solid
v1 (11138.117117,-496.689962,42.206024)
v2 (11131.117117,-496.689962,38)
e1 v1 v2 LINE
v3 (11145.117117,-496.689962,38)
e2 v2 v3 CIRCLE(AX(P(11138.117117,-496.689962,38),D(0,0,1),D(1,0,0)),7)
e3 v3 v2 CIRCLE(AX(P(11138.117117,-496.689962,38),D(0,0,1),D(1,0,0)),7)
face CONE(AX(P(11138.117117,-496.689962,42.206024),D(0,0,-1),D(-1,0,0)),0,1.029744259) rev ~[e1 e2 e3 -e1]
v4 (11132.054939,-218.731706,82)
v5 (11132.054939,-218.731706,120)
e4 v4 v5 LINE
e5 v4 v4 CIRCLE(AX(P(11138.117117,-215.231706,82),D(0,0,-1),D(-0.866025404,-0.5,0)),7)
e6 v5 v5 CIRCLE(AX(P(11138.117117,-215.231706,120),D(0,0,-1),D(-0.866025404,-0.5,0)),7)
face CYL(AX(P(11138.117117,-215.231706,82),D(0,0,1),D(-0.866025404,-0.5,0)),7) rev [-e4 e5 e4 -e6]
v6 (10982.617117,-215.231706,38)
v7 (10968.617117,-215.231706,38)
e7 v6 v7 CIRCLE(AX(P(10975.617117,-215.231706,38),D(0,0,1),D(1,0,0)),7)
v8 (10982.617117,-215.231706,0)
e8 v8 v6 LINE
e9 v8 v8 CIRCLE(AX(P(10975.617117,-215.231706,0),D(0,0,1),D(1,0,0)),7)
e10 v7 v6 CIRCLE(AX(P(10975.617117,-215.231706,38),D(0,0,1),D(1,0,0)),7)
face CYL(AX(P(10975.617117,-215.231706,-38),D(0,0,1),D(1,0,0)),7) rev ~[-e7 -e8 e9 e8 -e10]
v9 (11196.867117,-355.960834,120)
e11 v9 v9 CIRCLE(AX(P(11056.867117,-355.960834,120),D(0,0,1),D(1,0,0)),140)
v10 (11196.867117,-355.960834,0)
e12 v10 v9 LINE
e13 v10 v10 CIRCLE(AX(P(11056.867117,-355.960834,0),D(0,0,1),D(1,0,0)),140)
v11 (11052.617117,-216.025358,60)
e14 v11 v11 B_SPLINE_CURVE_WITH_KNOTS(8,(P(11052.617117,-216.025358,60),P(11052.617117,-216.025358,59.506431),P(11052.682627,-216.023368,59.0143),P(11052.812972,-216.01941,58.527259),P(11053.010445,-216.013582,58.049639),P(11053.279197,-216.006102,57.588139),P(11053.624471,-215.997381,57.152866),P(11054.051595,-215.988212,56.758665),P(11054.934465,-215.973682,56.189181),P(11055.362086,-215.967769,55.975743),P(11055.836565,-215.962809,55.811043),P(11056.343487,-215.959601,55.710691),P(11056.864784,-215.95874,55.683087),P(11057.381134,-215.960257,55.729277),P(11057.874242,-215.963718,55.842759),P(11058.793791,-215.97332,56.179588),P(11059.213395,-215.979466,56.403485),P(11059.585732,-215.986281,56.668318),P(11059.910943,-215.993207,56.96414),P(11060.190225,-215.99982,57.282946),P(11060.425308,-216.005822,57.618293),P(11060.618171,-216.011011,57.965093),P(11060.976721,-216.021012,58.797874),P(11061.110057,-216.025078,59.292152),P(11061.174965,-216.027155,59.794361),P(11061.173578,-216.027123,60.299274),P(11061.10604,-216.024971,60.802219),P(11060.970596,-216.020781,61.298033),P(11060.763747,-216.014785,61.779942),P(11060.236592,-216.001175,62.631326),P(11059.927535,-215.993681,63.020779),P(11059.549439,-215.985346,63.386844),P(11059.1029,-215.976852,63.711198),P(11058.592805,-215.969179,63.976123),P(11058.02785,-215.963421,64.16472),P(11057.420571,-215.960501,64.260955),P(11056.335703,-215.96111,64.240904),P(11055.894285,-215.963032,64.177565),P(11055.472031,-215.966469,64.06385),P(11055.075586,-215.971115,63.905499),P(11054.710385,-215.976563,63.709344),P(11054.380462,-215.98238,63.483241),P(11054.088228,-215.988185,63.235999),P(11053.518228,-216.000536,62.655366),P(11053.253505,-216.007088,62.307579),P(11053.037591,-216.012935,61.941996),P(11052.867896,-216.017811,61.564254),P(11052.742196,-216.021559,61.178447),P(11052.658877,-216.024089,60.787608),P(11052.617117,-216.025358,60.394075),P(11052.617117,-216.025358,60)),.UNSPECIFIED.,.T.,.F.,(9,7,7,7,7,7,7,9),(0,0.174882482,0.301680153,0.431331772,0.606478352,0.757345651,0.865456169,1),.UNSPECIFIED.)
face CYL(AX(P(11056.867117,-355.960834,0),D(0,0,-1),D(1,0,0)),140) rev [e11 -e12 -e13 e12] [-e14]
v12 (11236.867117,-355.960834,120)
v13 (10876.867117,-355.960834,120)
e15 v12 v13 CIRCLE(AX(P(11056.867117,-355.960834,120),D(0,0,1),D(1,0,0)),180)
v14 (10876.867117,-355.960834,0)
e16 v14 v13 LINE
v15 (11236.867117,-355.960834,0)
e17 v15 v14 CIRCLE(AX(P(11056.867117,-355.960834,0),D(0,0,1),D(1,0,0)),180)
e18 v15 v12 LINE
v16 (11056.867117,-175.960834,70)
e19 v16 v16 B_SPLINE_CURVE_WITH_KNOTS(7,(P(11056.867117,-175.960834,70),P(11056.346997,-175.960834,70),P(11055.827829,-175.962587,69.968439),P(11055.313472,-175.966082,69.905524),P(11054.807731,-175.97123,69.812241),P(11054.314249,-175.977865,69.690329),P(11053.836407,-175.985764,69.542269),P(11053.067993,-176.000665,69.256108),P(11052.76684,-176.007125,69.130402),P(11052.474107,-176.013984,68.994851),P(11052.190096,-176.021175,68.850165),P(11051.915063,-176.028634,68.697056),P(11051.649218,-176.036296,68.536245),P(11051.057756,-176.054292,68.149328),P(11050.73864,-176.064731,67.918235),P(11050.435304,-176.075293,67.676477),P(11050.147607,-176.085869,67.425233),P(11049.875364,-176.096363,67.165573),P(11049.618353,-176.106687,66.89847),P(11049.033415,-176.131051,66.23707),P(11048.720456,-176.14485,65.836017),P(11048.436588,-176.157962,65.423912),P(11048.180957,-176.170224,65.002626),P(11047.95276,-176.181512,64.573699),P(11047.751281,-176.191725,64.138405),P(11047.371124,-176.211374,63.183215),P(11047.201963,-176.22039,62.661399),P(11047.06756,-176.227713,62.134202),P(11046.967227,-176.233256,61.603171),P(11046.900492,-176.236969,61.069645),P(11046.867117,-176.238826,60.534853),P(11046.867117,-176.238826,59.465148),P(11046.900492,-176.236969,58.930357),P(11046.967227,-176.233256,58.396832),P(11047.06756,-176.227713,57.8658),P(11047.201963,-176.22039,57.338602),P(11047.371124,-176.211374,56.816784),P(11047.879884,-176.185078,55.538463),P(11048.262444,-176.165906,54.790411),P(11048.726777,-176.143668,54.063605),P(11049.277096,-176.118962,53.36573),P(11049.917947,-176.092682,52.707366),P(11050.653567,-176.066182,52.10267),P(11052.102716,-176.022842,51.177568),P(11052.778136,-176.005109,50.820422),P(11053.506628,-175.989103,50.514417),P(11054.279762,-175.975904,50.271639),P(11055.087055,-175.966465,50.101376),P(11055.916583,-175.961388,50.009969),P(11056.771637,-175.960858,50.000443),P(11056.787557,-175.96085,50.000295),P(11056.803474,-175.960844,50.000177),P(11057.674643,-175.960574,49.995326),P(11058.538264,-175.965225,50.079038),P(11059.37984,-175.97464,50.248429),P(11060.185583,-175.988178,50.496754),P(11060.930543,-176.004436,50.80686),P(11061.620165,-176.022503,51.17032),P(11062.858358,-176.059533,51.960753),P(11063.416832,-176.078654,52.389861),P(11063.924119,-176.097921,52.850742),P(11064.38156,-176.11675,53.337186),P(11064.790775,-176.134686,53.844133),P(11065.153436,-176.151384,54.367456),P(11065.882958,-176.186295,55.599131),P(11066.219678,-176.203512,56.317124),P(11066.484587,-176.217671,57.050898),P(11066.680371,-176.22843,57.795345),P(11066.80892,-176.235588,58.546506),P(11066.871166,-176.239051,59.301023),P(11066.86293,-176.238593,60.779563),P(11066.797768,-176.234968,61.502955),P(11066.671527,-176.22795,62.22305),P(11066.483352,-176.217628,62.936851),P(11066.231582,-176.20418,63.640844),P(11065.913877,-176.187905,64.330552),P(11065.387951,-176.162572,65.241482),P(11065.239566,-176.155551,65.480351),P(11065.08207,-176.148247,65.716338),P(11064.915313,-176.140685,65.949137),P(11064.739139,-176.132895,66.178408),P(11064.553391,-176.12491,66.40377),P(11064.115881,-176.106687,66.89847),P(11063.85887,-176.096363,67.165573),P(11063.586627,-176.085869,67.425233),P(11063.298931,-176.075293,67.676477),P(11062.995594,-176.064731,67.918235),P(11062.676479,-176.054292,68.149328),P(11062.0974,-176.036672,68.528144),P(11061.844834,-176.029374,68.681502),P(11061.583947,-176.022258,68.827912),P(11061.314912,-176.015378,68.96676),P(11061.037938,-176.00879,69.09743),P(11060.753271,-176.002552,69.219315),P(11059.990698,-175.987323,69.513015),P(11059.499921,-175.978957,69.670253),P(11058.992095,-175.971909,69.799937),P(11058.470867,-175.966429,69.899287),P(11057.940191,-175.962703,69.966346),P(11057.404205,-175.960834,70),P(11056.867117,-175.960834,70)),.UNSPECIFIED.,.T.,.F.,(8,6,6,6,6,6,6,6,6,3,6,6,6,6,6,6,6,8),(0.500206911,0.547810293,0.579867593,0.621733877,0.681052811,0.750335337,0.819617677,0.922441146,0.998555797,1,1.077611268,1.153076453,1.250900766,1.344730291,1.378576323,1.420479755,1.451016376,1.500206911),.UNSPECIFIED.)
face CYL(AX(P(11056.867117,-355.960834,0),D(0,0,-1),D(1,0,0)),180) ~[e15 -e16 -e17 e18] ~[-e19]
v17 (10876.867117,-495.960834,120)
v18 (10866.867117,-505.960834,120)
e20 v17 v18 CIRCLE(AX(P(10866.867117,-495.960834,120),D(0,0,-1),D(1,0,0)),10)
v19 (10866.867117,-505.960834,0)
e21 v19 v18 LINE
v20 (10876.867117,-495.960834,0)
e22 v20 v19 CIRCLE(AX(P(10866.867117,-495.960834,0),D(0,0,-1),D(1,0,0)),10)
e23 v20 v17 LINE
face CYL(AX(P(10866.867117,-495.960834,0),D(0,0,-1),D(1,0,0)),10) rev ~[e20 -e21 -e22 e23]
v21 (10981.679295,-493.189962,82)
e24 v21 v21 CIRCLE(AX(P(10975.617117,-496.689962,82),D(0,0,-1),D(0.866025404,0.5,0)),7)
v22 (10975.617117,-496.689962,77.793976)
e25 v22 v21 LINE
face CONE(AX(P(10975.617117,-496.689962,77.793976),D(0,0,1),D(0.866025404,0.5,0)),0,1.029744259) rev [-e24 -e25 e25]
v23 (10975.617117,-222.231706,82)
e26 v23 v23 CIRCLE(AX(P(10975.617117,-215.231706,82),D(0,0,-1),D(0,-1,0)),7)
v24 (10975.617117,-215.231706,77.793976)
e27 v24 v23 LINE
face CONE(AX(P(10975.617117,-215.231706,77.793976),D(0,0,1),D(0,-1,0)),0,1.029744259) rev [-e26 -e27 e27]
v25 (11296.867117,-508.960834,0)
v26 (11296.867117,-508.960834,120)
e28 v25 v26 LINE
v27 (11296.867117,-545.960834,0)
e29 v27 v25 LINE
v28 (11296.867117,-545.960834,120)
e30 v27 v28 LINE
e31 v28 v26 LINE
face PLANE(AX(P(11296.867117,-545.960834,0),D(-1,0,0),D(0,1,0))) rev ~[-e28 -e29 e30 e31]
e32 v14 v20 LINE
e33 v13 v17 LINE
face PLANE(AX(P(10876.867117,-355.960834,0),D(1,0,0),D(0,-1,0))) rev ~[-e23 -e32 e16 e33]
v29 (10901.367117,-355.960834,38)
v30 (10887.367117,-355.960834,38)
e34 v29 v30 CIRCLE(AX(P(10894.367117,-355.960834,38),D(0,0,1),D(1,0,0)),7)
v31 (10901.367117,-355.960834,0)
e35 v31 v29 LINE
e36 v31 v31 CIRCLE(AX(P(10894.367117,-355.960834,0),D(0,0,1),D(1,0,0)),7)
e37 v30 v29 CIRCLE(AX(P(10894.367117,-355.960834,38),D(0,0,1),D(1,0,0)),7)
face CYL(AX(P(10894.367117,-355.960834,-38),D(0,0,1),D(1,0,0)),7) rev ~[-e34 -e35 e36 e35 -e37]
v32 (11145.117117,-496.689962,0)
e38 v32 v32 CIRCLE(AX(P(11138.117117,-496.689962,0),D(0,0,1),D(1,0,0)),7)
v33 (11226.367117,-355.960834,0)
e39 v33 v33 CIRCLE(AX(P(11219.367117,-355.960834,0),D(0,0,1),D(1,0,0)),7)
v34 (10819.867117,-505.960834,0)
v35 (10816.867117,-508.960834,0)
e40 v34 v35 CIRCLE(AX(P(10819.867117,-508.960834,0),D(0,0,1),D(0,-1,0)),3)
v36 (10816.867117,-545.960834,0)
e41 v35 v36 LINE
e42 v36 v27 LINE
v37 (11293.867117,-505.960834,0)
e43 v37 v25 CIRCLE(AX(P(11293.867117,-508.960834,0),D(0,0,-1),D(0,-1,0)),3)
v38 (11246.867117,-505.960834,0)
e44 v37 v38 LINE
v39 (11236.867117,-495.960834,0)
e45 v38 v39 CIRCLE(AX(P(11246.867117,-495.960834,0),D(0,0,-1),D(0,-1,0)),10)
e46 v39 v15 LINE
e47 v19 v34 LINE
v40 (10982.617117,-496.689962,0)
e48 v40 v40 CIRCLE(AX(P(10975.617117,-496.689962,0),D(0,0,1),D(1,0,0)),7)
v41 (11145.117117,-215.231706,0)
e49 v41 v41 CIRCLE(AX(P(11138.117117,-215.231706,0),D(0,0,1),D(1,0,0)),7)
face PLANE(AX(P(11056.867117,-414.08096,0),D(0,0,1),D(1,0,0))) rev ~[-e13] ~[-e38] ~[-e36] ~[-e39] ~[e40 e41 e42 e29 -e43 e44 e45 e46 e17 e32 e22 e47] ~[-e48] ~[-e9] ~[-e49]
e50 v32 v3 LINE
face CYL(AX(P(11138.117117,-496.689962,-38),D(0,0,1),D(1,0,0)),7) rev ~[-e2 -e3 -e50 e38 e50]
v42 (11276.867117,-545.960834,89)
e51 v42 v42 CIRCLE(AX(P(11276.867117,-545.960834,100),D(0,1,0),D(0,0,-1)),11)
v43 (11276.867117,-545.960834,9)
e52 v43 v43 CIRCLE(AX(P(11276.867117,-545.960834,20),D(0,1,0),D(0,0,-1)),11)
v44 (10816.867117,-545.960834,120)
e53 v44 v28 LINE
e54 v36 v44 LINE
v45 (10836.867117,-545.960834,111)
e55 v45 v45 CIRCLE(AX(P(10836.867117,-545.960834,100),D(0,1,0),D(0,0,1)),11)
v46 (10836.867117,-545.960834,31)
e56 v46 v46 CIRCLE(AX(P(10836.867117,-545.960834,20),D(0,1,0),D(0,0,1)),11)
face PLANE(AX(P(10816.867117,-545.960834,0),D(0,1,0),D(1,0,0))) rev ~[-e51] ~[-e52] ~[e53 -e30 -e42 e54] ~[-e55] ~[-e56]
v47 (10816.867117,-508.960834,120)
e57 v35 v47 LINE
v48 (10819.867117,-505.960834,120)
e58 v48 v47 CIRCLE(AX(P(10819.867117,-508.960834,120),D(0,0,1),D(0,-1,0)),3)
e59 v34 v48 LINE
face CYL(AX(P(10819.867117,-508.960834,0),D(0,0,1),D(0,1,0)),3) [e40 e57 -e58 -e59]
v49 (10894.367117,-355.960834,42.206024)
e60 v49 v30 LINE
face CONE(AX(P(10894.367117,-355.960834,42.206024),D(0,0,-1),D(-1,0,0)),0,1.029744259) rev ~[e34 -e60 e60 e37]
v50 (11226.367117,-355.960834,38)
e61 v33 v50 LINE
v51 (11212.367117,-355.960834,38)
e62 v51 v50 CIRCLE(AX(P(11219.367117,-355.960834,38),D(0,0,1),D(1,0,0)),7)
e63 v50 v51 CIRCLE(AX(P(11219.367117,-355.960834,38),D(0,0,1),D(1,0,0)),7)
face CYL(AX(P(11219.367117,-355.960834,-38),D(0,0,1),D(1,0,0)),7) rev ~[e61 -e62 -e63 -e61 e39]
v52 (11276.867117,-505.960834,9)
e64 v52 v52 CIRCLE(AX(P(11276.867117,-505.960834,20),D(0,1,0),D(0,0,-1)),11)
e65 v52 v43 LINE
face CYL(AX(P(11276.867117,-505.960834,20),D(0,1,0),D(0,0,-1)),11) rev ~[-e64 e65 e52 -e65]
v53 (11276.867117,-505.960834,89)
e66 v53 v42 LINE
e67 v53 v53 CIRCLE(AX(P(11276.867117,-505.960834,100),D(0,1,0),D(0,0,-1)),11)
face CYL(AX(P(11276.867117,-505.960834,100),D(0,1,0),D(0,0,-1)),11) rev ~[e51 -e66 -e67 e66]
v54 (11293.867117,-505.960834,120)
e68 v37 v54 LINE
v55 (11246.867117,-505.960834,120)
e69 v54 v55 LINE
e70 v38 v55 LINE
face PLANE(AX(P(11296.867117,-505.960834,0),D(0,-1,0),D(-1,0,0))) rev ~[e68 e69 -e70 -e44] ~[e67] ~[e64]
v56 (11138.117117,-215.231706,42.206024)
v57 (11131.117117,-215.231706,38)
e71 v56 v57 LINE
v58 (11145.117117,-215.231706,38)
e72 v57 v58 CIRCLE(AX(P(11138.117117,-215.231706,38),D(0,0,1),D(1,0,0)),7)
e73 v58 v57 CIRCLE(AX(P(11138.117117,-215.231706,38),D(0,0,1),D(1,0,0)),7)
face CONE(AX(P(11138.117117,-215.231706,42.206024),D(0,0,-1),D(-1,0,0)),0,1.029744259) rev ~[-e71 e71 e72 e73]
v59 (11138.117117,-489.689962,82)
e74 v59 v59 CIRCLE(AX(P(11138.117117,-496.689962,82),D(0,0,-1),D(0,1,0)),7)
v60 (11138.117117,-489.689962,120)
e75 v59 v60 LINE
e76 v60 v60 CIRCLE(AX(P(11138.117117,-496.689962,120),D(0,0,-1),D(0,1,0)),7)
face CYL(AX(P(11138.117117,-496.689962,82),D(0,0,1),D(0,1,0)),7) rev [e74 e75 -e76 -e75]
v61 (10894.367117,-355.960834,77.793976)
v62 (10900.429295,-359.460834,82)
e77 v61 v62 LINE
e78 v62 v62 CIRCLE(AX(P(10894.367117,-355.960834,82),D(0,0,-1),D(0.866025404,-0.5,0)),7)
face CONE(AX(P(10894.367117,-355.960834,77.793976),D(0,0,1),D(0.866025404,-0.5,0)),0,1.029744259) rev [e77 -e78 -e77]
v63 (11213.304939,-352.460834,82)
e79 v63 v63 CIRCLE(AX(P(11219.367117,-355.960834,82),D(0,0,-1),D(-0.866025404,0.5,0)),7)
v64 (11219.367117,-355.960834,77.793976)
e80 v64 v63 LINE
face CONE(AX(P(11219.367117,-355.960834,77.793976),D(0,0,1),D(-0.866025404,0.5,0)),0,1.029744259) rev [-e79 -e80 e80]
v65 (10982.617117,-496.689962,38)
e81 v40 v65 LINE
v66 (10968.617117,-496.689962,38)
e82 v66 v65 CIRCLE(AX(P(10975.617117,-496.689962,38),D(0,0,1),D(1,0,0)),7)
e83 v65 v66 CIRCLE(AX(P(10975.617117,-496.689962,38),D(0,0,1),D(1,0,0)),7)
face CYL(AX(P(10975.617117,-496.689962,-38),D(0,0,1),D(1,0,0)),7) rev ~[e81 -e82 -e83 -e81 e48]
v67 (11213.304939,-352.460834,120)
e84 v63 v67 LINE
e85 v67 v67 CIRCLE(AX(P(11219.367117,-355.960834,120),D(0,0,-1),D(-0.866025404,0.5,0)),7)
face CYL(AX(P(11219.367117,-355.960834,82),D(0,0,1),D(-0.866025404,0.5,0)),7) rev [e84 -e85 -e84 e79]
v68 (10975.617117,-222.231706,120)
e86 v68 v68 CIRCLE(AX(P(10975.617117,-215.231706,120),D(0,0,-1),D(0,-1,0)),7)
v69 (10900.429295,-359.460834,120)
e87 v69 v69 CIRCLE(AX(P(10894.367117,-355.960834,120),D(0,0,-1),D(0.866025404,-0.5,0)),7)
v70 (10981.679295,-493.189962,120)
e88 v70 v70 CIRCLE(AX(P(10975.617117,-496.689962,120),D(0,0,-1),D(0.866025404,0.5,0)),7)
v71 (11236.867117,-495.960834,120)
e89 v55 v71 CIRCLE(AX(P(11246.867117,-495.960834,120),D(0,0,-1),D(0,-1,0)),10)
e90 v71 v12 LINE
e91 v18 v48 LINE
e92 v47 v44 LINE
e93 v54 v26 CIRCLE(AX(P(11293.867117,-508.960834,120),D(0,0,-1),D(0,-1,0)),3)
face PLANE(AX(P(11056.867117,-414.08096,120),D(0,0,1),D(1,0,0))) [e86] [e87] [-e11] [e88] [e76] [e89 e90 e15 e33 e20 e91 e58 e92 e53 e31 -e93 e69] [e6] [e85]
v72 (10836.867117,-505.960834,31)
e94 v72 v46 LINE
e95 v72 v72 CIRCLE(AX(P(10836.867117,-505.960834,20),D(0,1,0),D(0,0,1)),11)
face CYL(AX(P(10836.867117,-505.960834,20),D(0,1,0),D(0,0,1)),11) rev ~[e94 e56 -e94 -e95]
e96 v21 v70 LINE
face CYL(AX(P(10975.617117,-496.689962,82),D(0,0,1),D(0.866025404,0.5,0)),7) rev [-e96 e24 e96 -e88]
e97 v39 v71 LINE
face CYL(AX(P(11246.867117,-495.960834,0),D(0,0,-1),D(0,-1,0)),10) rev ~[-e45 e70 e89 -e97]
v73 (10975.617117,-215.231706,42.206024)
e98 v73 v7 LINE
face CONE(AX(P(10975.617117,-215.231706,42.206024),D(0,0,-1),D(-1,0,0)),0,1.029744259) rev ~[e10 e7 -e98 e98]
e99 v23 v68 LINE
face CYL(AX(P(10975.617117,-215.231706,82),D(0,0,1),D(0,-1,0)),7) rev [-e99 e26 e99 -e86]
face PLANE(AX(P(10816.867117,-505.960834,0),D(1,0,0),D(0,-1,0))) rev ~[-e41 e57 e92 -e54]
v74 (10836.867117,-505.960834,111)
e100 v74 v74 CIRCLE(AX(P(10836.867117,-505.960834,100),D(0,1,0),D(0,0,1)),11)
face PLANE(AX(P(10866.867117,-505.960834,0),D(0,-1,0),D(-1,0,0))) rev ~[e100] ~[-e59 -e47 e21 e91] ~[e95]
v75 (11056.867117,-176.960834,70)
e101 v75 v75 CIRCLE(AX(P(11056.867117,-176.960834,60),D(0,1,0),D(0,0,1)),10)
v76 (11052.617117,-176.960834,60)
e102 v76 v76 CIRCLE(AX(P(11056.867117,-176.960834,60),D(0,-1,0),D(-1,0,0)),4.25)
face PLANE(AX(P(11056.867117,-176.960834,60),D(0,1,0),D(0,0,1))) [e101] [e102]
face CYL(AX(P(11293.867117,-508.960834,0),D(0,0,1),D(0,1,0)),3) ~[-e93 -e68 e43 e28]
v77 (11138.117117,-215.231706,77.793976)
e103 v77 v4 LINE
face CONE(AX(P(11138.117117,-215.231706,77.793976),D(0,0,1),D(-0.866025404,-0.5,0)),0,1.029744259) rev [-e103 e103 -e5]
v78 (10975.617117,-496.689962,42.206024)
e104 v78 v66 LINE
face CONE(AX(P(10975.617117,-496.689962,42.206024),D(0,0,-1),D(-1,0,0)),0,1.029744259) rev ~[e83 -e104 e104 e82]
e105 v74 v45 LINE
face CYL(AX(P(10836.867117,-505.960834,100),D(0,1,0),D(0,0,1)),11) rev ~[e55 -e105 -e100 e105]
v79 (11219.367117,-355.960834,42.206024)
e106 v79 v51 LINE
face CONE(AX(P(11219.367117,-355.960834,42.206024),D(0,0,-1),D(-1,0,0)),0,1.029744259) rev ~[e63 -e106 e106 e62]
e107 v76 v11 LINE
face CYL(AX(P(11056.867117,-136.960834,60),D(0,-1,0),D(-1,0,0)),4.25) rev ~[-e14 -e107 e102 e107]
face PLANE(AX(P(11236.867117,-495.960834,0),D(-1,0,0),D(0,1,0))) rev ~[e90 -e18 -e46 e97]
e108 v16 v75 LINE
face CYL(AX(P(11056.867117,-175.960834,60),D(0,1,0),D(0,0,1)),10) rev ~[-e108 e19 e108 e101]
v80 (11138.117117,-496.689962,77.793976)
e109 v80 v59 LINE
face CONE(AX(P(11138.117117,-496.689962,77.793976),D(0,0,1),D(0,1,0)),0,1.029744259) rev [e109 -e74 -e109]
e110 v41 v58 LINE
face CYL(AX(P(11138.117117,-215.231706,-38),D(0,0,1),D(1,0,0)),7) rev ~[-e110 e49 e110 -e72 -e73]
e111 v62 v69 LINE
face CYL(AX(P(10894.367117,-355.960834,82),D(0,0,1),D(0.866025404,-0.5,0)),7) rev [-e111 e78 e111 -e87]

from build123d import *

# Parameters (mm, degrees)
SKETCH1_R              = 140
BOSS_EXTRUDE1_DEPTH    = 120
SKETCH3_R              = 10
CUT_EXTRUDE1_DEPTH     = 1
M10_TAPPED_HOLE1_D     = 8.5
M10_TAPPED_HOLE1_DEPTH = 40
M10_TAPPED_HOLE1_TIP   = 2.553657631
SKETCH7_R              = 11
CUT_EXTRUDE2_DEPTH     = 11303.32306496
FILLET1_R              = 3
CIRPATTERN1_COUNT      = 6
M16_TAPPED_HOLE2_D     = 14
M16_TAPPED_HOLE2_DEPTH = 38
M16_TAPPED_HOLE2_TIP   = 4.206024333


with BuildPart() as part:
    # Sketch1 → Boss-Extrude1 (new body)
    with BuildSketch(Plane.XY):
        with BuildLine():
            Line((10876.867117242, -355.960833708), (10876.867117242, -495.960833708))
            ThreePointArc((10876.867117242, -495.960833708), (10873.938185054, -503.03190152), (10866.867117242, -505.960833708))
            Line((10866.867117242, -505.960833708), (10816.867117242, -505.960833708))
            Line((10816.867117242, -505.960833708), (10816.867117242, -545.960833708))
            Line((10816.867117242, -545.960833708), (11296.867117242, -545.960833708))
            Line((11296.867117242, -545.960833708), (11296.867117242, -505.960833708))
            Line((11296.867117242, -505.960833708), (11246.867117242, -505.960833708))
            ThreePointArc((11246.867117242, -505.960833708), (11239.796049431, -503.03190152), (11236.867117242, -495.960833708))
            Line((11236.867117242, -495.960833708), (11236.867117242, -355.960833708))
            ThreePointArc((11236.867117242, -355.960833708), (11056.867117242, -175.960833708), (10876.867117242, -355.960833708))
        make_face()
        with Locations((11056.867117242, -355.960833708)):
            Circle(SKETCH1_R, mode=Mode.SUBTRACT)
    extrude(amount=BOSS_EXTRUDE1_DEPTH)

    # Sketch3 → Cut-Extrude1 (cut)
    with BuildSketch(Plane(origin=(0, -175.960833708, 0), x_dir=(1, 0, 0), z_dir=(0, 1, 0))):
        with Locations(Location((11056.867117242, -60, 0), (0, 0, 270))):
            Circle(SKETCH3_R)
    extrude(amount=-CUT_EXTRUDE1_DEPTH, mode=Mode.SUBTRACT)

    # M10 Tapped Hole1
    with Locations(Plane(origin=(0, -176.960833708, 0), x_dir=(1, 0, 0), z_dir=(0, 1, 0))):
        with Locations((11056.867117242, -60)):
            Hole(M10_TAPPED_HOLE1_D / 2, depth=M10_TAPPED_HOLE1_DEPTH)
            with Locations((0, 0, -(M10_TAPPED_HOLE1_DEPTH + M10_TAPPED_HOLE1_TIP / 2))):  # 118° drill point
                Cone(0, M10_TAPPED_HOLE1_D / 2, M10_TAPPED_HOLE1_TIP, mode=Mode.SUBTRACT)

    # Sketch7 → Cut-Extrude2 (cut, through all)
    with BuildSketch(Plane(origin=(0, -505.960833708, 0), x_dir=(1, 0, 0), z_dir=(0, 1, 0))):
        with Locations(Location((10836.867117242, -20, 0), (0, 0, 270))):
            Circle(SKETCH7_R)
        with Locations(Location((10836.867117242, -100, 0), (0, 0, 270))):
            Circle(SKETCH7_R)
        with Locations(Location((11276.867117242, -100, 0), (0, 0, 90))):
            Circle(SKETCH7_R)
        with Locations(Location((11276.867117242, -20, 0), (0, 0, 90))):
            Circle(SKETCH7_R)
    extrude(amount=-CUT_EXTRUDE2_DEPTH, mode=Mode.SUBTRACT)

    # Fillet1
    fillet1_edges = [part.edges().sort_by_distance(p)[0] for p in [
        (11296.867117242, -505.960833708, 60),
        (10816.867117242, -505.960833708, 60),
    ]]
    fillet(fillet1_edges, radius=FILLET1_R)

    # Sketch9 → M16 Tapped Hole1 (revolve, cut)
    with BuildSketch(Plane(origin=(10975.617117242, -215.231705593, 120), x_dir=(0, -1, 0), z_dir=(1, 0, 0))):
        Polygon((0, 0), (0, 42.206024333), (7, 38), (7, 0), align=None)
    m16_tapped_hole1 = revolve(axis=Axis((10975.617117242, -215.231705593, 126.35), (0, 0, -1)), mode=Mode.SUBTRACT)

    # CirPattern1: M16 Tapped Hole1 ×6 about axis
    cirpattern1_axis = Axis((11056.867117242, -355.960833708, 0), (0, 0, 1))
    for i in range(1, CIRPATTERN1_COUNT):
        add(m16_tapped_hole1.rotate(cirpattern1_axis, i * 360 / CIRPATTERN1_COUNT), mode=Mode.SUBTRACT)

    # M16 Tapped Hole2
    with Locations(Plane(origin=(0, 0, 0), x_dir=(-1, 0, 0), z_dir=(0, 0, -1))):
        with Locations((-11138.117117242, -215.231705593), (-10975.617117242, -215.231705593), (-10894.367117242, -355.960833708), (-10975.617117242, -496.689961823), (-11138.117117242, -496.689961823), (-11219.367117242, -355.960833708)):
            Hole(M16_TAPPED_HOLE2_D / 2, depth=M16_TAPPED_HOLE2_DEPTH)
            with Locations((0, 0, -(M16_TAPPED_HOLE2_DEPTH + M16_TAPPED_HOLE2_TIP / 2))):  # 118° drill point
                Cone(0, M16_TAPPED_HOLE2_D / 2, M16_TAPPED_HOLE2_TIP, mode=Mode.SUBTRACT)


solid = part.part
